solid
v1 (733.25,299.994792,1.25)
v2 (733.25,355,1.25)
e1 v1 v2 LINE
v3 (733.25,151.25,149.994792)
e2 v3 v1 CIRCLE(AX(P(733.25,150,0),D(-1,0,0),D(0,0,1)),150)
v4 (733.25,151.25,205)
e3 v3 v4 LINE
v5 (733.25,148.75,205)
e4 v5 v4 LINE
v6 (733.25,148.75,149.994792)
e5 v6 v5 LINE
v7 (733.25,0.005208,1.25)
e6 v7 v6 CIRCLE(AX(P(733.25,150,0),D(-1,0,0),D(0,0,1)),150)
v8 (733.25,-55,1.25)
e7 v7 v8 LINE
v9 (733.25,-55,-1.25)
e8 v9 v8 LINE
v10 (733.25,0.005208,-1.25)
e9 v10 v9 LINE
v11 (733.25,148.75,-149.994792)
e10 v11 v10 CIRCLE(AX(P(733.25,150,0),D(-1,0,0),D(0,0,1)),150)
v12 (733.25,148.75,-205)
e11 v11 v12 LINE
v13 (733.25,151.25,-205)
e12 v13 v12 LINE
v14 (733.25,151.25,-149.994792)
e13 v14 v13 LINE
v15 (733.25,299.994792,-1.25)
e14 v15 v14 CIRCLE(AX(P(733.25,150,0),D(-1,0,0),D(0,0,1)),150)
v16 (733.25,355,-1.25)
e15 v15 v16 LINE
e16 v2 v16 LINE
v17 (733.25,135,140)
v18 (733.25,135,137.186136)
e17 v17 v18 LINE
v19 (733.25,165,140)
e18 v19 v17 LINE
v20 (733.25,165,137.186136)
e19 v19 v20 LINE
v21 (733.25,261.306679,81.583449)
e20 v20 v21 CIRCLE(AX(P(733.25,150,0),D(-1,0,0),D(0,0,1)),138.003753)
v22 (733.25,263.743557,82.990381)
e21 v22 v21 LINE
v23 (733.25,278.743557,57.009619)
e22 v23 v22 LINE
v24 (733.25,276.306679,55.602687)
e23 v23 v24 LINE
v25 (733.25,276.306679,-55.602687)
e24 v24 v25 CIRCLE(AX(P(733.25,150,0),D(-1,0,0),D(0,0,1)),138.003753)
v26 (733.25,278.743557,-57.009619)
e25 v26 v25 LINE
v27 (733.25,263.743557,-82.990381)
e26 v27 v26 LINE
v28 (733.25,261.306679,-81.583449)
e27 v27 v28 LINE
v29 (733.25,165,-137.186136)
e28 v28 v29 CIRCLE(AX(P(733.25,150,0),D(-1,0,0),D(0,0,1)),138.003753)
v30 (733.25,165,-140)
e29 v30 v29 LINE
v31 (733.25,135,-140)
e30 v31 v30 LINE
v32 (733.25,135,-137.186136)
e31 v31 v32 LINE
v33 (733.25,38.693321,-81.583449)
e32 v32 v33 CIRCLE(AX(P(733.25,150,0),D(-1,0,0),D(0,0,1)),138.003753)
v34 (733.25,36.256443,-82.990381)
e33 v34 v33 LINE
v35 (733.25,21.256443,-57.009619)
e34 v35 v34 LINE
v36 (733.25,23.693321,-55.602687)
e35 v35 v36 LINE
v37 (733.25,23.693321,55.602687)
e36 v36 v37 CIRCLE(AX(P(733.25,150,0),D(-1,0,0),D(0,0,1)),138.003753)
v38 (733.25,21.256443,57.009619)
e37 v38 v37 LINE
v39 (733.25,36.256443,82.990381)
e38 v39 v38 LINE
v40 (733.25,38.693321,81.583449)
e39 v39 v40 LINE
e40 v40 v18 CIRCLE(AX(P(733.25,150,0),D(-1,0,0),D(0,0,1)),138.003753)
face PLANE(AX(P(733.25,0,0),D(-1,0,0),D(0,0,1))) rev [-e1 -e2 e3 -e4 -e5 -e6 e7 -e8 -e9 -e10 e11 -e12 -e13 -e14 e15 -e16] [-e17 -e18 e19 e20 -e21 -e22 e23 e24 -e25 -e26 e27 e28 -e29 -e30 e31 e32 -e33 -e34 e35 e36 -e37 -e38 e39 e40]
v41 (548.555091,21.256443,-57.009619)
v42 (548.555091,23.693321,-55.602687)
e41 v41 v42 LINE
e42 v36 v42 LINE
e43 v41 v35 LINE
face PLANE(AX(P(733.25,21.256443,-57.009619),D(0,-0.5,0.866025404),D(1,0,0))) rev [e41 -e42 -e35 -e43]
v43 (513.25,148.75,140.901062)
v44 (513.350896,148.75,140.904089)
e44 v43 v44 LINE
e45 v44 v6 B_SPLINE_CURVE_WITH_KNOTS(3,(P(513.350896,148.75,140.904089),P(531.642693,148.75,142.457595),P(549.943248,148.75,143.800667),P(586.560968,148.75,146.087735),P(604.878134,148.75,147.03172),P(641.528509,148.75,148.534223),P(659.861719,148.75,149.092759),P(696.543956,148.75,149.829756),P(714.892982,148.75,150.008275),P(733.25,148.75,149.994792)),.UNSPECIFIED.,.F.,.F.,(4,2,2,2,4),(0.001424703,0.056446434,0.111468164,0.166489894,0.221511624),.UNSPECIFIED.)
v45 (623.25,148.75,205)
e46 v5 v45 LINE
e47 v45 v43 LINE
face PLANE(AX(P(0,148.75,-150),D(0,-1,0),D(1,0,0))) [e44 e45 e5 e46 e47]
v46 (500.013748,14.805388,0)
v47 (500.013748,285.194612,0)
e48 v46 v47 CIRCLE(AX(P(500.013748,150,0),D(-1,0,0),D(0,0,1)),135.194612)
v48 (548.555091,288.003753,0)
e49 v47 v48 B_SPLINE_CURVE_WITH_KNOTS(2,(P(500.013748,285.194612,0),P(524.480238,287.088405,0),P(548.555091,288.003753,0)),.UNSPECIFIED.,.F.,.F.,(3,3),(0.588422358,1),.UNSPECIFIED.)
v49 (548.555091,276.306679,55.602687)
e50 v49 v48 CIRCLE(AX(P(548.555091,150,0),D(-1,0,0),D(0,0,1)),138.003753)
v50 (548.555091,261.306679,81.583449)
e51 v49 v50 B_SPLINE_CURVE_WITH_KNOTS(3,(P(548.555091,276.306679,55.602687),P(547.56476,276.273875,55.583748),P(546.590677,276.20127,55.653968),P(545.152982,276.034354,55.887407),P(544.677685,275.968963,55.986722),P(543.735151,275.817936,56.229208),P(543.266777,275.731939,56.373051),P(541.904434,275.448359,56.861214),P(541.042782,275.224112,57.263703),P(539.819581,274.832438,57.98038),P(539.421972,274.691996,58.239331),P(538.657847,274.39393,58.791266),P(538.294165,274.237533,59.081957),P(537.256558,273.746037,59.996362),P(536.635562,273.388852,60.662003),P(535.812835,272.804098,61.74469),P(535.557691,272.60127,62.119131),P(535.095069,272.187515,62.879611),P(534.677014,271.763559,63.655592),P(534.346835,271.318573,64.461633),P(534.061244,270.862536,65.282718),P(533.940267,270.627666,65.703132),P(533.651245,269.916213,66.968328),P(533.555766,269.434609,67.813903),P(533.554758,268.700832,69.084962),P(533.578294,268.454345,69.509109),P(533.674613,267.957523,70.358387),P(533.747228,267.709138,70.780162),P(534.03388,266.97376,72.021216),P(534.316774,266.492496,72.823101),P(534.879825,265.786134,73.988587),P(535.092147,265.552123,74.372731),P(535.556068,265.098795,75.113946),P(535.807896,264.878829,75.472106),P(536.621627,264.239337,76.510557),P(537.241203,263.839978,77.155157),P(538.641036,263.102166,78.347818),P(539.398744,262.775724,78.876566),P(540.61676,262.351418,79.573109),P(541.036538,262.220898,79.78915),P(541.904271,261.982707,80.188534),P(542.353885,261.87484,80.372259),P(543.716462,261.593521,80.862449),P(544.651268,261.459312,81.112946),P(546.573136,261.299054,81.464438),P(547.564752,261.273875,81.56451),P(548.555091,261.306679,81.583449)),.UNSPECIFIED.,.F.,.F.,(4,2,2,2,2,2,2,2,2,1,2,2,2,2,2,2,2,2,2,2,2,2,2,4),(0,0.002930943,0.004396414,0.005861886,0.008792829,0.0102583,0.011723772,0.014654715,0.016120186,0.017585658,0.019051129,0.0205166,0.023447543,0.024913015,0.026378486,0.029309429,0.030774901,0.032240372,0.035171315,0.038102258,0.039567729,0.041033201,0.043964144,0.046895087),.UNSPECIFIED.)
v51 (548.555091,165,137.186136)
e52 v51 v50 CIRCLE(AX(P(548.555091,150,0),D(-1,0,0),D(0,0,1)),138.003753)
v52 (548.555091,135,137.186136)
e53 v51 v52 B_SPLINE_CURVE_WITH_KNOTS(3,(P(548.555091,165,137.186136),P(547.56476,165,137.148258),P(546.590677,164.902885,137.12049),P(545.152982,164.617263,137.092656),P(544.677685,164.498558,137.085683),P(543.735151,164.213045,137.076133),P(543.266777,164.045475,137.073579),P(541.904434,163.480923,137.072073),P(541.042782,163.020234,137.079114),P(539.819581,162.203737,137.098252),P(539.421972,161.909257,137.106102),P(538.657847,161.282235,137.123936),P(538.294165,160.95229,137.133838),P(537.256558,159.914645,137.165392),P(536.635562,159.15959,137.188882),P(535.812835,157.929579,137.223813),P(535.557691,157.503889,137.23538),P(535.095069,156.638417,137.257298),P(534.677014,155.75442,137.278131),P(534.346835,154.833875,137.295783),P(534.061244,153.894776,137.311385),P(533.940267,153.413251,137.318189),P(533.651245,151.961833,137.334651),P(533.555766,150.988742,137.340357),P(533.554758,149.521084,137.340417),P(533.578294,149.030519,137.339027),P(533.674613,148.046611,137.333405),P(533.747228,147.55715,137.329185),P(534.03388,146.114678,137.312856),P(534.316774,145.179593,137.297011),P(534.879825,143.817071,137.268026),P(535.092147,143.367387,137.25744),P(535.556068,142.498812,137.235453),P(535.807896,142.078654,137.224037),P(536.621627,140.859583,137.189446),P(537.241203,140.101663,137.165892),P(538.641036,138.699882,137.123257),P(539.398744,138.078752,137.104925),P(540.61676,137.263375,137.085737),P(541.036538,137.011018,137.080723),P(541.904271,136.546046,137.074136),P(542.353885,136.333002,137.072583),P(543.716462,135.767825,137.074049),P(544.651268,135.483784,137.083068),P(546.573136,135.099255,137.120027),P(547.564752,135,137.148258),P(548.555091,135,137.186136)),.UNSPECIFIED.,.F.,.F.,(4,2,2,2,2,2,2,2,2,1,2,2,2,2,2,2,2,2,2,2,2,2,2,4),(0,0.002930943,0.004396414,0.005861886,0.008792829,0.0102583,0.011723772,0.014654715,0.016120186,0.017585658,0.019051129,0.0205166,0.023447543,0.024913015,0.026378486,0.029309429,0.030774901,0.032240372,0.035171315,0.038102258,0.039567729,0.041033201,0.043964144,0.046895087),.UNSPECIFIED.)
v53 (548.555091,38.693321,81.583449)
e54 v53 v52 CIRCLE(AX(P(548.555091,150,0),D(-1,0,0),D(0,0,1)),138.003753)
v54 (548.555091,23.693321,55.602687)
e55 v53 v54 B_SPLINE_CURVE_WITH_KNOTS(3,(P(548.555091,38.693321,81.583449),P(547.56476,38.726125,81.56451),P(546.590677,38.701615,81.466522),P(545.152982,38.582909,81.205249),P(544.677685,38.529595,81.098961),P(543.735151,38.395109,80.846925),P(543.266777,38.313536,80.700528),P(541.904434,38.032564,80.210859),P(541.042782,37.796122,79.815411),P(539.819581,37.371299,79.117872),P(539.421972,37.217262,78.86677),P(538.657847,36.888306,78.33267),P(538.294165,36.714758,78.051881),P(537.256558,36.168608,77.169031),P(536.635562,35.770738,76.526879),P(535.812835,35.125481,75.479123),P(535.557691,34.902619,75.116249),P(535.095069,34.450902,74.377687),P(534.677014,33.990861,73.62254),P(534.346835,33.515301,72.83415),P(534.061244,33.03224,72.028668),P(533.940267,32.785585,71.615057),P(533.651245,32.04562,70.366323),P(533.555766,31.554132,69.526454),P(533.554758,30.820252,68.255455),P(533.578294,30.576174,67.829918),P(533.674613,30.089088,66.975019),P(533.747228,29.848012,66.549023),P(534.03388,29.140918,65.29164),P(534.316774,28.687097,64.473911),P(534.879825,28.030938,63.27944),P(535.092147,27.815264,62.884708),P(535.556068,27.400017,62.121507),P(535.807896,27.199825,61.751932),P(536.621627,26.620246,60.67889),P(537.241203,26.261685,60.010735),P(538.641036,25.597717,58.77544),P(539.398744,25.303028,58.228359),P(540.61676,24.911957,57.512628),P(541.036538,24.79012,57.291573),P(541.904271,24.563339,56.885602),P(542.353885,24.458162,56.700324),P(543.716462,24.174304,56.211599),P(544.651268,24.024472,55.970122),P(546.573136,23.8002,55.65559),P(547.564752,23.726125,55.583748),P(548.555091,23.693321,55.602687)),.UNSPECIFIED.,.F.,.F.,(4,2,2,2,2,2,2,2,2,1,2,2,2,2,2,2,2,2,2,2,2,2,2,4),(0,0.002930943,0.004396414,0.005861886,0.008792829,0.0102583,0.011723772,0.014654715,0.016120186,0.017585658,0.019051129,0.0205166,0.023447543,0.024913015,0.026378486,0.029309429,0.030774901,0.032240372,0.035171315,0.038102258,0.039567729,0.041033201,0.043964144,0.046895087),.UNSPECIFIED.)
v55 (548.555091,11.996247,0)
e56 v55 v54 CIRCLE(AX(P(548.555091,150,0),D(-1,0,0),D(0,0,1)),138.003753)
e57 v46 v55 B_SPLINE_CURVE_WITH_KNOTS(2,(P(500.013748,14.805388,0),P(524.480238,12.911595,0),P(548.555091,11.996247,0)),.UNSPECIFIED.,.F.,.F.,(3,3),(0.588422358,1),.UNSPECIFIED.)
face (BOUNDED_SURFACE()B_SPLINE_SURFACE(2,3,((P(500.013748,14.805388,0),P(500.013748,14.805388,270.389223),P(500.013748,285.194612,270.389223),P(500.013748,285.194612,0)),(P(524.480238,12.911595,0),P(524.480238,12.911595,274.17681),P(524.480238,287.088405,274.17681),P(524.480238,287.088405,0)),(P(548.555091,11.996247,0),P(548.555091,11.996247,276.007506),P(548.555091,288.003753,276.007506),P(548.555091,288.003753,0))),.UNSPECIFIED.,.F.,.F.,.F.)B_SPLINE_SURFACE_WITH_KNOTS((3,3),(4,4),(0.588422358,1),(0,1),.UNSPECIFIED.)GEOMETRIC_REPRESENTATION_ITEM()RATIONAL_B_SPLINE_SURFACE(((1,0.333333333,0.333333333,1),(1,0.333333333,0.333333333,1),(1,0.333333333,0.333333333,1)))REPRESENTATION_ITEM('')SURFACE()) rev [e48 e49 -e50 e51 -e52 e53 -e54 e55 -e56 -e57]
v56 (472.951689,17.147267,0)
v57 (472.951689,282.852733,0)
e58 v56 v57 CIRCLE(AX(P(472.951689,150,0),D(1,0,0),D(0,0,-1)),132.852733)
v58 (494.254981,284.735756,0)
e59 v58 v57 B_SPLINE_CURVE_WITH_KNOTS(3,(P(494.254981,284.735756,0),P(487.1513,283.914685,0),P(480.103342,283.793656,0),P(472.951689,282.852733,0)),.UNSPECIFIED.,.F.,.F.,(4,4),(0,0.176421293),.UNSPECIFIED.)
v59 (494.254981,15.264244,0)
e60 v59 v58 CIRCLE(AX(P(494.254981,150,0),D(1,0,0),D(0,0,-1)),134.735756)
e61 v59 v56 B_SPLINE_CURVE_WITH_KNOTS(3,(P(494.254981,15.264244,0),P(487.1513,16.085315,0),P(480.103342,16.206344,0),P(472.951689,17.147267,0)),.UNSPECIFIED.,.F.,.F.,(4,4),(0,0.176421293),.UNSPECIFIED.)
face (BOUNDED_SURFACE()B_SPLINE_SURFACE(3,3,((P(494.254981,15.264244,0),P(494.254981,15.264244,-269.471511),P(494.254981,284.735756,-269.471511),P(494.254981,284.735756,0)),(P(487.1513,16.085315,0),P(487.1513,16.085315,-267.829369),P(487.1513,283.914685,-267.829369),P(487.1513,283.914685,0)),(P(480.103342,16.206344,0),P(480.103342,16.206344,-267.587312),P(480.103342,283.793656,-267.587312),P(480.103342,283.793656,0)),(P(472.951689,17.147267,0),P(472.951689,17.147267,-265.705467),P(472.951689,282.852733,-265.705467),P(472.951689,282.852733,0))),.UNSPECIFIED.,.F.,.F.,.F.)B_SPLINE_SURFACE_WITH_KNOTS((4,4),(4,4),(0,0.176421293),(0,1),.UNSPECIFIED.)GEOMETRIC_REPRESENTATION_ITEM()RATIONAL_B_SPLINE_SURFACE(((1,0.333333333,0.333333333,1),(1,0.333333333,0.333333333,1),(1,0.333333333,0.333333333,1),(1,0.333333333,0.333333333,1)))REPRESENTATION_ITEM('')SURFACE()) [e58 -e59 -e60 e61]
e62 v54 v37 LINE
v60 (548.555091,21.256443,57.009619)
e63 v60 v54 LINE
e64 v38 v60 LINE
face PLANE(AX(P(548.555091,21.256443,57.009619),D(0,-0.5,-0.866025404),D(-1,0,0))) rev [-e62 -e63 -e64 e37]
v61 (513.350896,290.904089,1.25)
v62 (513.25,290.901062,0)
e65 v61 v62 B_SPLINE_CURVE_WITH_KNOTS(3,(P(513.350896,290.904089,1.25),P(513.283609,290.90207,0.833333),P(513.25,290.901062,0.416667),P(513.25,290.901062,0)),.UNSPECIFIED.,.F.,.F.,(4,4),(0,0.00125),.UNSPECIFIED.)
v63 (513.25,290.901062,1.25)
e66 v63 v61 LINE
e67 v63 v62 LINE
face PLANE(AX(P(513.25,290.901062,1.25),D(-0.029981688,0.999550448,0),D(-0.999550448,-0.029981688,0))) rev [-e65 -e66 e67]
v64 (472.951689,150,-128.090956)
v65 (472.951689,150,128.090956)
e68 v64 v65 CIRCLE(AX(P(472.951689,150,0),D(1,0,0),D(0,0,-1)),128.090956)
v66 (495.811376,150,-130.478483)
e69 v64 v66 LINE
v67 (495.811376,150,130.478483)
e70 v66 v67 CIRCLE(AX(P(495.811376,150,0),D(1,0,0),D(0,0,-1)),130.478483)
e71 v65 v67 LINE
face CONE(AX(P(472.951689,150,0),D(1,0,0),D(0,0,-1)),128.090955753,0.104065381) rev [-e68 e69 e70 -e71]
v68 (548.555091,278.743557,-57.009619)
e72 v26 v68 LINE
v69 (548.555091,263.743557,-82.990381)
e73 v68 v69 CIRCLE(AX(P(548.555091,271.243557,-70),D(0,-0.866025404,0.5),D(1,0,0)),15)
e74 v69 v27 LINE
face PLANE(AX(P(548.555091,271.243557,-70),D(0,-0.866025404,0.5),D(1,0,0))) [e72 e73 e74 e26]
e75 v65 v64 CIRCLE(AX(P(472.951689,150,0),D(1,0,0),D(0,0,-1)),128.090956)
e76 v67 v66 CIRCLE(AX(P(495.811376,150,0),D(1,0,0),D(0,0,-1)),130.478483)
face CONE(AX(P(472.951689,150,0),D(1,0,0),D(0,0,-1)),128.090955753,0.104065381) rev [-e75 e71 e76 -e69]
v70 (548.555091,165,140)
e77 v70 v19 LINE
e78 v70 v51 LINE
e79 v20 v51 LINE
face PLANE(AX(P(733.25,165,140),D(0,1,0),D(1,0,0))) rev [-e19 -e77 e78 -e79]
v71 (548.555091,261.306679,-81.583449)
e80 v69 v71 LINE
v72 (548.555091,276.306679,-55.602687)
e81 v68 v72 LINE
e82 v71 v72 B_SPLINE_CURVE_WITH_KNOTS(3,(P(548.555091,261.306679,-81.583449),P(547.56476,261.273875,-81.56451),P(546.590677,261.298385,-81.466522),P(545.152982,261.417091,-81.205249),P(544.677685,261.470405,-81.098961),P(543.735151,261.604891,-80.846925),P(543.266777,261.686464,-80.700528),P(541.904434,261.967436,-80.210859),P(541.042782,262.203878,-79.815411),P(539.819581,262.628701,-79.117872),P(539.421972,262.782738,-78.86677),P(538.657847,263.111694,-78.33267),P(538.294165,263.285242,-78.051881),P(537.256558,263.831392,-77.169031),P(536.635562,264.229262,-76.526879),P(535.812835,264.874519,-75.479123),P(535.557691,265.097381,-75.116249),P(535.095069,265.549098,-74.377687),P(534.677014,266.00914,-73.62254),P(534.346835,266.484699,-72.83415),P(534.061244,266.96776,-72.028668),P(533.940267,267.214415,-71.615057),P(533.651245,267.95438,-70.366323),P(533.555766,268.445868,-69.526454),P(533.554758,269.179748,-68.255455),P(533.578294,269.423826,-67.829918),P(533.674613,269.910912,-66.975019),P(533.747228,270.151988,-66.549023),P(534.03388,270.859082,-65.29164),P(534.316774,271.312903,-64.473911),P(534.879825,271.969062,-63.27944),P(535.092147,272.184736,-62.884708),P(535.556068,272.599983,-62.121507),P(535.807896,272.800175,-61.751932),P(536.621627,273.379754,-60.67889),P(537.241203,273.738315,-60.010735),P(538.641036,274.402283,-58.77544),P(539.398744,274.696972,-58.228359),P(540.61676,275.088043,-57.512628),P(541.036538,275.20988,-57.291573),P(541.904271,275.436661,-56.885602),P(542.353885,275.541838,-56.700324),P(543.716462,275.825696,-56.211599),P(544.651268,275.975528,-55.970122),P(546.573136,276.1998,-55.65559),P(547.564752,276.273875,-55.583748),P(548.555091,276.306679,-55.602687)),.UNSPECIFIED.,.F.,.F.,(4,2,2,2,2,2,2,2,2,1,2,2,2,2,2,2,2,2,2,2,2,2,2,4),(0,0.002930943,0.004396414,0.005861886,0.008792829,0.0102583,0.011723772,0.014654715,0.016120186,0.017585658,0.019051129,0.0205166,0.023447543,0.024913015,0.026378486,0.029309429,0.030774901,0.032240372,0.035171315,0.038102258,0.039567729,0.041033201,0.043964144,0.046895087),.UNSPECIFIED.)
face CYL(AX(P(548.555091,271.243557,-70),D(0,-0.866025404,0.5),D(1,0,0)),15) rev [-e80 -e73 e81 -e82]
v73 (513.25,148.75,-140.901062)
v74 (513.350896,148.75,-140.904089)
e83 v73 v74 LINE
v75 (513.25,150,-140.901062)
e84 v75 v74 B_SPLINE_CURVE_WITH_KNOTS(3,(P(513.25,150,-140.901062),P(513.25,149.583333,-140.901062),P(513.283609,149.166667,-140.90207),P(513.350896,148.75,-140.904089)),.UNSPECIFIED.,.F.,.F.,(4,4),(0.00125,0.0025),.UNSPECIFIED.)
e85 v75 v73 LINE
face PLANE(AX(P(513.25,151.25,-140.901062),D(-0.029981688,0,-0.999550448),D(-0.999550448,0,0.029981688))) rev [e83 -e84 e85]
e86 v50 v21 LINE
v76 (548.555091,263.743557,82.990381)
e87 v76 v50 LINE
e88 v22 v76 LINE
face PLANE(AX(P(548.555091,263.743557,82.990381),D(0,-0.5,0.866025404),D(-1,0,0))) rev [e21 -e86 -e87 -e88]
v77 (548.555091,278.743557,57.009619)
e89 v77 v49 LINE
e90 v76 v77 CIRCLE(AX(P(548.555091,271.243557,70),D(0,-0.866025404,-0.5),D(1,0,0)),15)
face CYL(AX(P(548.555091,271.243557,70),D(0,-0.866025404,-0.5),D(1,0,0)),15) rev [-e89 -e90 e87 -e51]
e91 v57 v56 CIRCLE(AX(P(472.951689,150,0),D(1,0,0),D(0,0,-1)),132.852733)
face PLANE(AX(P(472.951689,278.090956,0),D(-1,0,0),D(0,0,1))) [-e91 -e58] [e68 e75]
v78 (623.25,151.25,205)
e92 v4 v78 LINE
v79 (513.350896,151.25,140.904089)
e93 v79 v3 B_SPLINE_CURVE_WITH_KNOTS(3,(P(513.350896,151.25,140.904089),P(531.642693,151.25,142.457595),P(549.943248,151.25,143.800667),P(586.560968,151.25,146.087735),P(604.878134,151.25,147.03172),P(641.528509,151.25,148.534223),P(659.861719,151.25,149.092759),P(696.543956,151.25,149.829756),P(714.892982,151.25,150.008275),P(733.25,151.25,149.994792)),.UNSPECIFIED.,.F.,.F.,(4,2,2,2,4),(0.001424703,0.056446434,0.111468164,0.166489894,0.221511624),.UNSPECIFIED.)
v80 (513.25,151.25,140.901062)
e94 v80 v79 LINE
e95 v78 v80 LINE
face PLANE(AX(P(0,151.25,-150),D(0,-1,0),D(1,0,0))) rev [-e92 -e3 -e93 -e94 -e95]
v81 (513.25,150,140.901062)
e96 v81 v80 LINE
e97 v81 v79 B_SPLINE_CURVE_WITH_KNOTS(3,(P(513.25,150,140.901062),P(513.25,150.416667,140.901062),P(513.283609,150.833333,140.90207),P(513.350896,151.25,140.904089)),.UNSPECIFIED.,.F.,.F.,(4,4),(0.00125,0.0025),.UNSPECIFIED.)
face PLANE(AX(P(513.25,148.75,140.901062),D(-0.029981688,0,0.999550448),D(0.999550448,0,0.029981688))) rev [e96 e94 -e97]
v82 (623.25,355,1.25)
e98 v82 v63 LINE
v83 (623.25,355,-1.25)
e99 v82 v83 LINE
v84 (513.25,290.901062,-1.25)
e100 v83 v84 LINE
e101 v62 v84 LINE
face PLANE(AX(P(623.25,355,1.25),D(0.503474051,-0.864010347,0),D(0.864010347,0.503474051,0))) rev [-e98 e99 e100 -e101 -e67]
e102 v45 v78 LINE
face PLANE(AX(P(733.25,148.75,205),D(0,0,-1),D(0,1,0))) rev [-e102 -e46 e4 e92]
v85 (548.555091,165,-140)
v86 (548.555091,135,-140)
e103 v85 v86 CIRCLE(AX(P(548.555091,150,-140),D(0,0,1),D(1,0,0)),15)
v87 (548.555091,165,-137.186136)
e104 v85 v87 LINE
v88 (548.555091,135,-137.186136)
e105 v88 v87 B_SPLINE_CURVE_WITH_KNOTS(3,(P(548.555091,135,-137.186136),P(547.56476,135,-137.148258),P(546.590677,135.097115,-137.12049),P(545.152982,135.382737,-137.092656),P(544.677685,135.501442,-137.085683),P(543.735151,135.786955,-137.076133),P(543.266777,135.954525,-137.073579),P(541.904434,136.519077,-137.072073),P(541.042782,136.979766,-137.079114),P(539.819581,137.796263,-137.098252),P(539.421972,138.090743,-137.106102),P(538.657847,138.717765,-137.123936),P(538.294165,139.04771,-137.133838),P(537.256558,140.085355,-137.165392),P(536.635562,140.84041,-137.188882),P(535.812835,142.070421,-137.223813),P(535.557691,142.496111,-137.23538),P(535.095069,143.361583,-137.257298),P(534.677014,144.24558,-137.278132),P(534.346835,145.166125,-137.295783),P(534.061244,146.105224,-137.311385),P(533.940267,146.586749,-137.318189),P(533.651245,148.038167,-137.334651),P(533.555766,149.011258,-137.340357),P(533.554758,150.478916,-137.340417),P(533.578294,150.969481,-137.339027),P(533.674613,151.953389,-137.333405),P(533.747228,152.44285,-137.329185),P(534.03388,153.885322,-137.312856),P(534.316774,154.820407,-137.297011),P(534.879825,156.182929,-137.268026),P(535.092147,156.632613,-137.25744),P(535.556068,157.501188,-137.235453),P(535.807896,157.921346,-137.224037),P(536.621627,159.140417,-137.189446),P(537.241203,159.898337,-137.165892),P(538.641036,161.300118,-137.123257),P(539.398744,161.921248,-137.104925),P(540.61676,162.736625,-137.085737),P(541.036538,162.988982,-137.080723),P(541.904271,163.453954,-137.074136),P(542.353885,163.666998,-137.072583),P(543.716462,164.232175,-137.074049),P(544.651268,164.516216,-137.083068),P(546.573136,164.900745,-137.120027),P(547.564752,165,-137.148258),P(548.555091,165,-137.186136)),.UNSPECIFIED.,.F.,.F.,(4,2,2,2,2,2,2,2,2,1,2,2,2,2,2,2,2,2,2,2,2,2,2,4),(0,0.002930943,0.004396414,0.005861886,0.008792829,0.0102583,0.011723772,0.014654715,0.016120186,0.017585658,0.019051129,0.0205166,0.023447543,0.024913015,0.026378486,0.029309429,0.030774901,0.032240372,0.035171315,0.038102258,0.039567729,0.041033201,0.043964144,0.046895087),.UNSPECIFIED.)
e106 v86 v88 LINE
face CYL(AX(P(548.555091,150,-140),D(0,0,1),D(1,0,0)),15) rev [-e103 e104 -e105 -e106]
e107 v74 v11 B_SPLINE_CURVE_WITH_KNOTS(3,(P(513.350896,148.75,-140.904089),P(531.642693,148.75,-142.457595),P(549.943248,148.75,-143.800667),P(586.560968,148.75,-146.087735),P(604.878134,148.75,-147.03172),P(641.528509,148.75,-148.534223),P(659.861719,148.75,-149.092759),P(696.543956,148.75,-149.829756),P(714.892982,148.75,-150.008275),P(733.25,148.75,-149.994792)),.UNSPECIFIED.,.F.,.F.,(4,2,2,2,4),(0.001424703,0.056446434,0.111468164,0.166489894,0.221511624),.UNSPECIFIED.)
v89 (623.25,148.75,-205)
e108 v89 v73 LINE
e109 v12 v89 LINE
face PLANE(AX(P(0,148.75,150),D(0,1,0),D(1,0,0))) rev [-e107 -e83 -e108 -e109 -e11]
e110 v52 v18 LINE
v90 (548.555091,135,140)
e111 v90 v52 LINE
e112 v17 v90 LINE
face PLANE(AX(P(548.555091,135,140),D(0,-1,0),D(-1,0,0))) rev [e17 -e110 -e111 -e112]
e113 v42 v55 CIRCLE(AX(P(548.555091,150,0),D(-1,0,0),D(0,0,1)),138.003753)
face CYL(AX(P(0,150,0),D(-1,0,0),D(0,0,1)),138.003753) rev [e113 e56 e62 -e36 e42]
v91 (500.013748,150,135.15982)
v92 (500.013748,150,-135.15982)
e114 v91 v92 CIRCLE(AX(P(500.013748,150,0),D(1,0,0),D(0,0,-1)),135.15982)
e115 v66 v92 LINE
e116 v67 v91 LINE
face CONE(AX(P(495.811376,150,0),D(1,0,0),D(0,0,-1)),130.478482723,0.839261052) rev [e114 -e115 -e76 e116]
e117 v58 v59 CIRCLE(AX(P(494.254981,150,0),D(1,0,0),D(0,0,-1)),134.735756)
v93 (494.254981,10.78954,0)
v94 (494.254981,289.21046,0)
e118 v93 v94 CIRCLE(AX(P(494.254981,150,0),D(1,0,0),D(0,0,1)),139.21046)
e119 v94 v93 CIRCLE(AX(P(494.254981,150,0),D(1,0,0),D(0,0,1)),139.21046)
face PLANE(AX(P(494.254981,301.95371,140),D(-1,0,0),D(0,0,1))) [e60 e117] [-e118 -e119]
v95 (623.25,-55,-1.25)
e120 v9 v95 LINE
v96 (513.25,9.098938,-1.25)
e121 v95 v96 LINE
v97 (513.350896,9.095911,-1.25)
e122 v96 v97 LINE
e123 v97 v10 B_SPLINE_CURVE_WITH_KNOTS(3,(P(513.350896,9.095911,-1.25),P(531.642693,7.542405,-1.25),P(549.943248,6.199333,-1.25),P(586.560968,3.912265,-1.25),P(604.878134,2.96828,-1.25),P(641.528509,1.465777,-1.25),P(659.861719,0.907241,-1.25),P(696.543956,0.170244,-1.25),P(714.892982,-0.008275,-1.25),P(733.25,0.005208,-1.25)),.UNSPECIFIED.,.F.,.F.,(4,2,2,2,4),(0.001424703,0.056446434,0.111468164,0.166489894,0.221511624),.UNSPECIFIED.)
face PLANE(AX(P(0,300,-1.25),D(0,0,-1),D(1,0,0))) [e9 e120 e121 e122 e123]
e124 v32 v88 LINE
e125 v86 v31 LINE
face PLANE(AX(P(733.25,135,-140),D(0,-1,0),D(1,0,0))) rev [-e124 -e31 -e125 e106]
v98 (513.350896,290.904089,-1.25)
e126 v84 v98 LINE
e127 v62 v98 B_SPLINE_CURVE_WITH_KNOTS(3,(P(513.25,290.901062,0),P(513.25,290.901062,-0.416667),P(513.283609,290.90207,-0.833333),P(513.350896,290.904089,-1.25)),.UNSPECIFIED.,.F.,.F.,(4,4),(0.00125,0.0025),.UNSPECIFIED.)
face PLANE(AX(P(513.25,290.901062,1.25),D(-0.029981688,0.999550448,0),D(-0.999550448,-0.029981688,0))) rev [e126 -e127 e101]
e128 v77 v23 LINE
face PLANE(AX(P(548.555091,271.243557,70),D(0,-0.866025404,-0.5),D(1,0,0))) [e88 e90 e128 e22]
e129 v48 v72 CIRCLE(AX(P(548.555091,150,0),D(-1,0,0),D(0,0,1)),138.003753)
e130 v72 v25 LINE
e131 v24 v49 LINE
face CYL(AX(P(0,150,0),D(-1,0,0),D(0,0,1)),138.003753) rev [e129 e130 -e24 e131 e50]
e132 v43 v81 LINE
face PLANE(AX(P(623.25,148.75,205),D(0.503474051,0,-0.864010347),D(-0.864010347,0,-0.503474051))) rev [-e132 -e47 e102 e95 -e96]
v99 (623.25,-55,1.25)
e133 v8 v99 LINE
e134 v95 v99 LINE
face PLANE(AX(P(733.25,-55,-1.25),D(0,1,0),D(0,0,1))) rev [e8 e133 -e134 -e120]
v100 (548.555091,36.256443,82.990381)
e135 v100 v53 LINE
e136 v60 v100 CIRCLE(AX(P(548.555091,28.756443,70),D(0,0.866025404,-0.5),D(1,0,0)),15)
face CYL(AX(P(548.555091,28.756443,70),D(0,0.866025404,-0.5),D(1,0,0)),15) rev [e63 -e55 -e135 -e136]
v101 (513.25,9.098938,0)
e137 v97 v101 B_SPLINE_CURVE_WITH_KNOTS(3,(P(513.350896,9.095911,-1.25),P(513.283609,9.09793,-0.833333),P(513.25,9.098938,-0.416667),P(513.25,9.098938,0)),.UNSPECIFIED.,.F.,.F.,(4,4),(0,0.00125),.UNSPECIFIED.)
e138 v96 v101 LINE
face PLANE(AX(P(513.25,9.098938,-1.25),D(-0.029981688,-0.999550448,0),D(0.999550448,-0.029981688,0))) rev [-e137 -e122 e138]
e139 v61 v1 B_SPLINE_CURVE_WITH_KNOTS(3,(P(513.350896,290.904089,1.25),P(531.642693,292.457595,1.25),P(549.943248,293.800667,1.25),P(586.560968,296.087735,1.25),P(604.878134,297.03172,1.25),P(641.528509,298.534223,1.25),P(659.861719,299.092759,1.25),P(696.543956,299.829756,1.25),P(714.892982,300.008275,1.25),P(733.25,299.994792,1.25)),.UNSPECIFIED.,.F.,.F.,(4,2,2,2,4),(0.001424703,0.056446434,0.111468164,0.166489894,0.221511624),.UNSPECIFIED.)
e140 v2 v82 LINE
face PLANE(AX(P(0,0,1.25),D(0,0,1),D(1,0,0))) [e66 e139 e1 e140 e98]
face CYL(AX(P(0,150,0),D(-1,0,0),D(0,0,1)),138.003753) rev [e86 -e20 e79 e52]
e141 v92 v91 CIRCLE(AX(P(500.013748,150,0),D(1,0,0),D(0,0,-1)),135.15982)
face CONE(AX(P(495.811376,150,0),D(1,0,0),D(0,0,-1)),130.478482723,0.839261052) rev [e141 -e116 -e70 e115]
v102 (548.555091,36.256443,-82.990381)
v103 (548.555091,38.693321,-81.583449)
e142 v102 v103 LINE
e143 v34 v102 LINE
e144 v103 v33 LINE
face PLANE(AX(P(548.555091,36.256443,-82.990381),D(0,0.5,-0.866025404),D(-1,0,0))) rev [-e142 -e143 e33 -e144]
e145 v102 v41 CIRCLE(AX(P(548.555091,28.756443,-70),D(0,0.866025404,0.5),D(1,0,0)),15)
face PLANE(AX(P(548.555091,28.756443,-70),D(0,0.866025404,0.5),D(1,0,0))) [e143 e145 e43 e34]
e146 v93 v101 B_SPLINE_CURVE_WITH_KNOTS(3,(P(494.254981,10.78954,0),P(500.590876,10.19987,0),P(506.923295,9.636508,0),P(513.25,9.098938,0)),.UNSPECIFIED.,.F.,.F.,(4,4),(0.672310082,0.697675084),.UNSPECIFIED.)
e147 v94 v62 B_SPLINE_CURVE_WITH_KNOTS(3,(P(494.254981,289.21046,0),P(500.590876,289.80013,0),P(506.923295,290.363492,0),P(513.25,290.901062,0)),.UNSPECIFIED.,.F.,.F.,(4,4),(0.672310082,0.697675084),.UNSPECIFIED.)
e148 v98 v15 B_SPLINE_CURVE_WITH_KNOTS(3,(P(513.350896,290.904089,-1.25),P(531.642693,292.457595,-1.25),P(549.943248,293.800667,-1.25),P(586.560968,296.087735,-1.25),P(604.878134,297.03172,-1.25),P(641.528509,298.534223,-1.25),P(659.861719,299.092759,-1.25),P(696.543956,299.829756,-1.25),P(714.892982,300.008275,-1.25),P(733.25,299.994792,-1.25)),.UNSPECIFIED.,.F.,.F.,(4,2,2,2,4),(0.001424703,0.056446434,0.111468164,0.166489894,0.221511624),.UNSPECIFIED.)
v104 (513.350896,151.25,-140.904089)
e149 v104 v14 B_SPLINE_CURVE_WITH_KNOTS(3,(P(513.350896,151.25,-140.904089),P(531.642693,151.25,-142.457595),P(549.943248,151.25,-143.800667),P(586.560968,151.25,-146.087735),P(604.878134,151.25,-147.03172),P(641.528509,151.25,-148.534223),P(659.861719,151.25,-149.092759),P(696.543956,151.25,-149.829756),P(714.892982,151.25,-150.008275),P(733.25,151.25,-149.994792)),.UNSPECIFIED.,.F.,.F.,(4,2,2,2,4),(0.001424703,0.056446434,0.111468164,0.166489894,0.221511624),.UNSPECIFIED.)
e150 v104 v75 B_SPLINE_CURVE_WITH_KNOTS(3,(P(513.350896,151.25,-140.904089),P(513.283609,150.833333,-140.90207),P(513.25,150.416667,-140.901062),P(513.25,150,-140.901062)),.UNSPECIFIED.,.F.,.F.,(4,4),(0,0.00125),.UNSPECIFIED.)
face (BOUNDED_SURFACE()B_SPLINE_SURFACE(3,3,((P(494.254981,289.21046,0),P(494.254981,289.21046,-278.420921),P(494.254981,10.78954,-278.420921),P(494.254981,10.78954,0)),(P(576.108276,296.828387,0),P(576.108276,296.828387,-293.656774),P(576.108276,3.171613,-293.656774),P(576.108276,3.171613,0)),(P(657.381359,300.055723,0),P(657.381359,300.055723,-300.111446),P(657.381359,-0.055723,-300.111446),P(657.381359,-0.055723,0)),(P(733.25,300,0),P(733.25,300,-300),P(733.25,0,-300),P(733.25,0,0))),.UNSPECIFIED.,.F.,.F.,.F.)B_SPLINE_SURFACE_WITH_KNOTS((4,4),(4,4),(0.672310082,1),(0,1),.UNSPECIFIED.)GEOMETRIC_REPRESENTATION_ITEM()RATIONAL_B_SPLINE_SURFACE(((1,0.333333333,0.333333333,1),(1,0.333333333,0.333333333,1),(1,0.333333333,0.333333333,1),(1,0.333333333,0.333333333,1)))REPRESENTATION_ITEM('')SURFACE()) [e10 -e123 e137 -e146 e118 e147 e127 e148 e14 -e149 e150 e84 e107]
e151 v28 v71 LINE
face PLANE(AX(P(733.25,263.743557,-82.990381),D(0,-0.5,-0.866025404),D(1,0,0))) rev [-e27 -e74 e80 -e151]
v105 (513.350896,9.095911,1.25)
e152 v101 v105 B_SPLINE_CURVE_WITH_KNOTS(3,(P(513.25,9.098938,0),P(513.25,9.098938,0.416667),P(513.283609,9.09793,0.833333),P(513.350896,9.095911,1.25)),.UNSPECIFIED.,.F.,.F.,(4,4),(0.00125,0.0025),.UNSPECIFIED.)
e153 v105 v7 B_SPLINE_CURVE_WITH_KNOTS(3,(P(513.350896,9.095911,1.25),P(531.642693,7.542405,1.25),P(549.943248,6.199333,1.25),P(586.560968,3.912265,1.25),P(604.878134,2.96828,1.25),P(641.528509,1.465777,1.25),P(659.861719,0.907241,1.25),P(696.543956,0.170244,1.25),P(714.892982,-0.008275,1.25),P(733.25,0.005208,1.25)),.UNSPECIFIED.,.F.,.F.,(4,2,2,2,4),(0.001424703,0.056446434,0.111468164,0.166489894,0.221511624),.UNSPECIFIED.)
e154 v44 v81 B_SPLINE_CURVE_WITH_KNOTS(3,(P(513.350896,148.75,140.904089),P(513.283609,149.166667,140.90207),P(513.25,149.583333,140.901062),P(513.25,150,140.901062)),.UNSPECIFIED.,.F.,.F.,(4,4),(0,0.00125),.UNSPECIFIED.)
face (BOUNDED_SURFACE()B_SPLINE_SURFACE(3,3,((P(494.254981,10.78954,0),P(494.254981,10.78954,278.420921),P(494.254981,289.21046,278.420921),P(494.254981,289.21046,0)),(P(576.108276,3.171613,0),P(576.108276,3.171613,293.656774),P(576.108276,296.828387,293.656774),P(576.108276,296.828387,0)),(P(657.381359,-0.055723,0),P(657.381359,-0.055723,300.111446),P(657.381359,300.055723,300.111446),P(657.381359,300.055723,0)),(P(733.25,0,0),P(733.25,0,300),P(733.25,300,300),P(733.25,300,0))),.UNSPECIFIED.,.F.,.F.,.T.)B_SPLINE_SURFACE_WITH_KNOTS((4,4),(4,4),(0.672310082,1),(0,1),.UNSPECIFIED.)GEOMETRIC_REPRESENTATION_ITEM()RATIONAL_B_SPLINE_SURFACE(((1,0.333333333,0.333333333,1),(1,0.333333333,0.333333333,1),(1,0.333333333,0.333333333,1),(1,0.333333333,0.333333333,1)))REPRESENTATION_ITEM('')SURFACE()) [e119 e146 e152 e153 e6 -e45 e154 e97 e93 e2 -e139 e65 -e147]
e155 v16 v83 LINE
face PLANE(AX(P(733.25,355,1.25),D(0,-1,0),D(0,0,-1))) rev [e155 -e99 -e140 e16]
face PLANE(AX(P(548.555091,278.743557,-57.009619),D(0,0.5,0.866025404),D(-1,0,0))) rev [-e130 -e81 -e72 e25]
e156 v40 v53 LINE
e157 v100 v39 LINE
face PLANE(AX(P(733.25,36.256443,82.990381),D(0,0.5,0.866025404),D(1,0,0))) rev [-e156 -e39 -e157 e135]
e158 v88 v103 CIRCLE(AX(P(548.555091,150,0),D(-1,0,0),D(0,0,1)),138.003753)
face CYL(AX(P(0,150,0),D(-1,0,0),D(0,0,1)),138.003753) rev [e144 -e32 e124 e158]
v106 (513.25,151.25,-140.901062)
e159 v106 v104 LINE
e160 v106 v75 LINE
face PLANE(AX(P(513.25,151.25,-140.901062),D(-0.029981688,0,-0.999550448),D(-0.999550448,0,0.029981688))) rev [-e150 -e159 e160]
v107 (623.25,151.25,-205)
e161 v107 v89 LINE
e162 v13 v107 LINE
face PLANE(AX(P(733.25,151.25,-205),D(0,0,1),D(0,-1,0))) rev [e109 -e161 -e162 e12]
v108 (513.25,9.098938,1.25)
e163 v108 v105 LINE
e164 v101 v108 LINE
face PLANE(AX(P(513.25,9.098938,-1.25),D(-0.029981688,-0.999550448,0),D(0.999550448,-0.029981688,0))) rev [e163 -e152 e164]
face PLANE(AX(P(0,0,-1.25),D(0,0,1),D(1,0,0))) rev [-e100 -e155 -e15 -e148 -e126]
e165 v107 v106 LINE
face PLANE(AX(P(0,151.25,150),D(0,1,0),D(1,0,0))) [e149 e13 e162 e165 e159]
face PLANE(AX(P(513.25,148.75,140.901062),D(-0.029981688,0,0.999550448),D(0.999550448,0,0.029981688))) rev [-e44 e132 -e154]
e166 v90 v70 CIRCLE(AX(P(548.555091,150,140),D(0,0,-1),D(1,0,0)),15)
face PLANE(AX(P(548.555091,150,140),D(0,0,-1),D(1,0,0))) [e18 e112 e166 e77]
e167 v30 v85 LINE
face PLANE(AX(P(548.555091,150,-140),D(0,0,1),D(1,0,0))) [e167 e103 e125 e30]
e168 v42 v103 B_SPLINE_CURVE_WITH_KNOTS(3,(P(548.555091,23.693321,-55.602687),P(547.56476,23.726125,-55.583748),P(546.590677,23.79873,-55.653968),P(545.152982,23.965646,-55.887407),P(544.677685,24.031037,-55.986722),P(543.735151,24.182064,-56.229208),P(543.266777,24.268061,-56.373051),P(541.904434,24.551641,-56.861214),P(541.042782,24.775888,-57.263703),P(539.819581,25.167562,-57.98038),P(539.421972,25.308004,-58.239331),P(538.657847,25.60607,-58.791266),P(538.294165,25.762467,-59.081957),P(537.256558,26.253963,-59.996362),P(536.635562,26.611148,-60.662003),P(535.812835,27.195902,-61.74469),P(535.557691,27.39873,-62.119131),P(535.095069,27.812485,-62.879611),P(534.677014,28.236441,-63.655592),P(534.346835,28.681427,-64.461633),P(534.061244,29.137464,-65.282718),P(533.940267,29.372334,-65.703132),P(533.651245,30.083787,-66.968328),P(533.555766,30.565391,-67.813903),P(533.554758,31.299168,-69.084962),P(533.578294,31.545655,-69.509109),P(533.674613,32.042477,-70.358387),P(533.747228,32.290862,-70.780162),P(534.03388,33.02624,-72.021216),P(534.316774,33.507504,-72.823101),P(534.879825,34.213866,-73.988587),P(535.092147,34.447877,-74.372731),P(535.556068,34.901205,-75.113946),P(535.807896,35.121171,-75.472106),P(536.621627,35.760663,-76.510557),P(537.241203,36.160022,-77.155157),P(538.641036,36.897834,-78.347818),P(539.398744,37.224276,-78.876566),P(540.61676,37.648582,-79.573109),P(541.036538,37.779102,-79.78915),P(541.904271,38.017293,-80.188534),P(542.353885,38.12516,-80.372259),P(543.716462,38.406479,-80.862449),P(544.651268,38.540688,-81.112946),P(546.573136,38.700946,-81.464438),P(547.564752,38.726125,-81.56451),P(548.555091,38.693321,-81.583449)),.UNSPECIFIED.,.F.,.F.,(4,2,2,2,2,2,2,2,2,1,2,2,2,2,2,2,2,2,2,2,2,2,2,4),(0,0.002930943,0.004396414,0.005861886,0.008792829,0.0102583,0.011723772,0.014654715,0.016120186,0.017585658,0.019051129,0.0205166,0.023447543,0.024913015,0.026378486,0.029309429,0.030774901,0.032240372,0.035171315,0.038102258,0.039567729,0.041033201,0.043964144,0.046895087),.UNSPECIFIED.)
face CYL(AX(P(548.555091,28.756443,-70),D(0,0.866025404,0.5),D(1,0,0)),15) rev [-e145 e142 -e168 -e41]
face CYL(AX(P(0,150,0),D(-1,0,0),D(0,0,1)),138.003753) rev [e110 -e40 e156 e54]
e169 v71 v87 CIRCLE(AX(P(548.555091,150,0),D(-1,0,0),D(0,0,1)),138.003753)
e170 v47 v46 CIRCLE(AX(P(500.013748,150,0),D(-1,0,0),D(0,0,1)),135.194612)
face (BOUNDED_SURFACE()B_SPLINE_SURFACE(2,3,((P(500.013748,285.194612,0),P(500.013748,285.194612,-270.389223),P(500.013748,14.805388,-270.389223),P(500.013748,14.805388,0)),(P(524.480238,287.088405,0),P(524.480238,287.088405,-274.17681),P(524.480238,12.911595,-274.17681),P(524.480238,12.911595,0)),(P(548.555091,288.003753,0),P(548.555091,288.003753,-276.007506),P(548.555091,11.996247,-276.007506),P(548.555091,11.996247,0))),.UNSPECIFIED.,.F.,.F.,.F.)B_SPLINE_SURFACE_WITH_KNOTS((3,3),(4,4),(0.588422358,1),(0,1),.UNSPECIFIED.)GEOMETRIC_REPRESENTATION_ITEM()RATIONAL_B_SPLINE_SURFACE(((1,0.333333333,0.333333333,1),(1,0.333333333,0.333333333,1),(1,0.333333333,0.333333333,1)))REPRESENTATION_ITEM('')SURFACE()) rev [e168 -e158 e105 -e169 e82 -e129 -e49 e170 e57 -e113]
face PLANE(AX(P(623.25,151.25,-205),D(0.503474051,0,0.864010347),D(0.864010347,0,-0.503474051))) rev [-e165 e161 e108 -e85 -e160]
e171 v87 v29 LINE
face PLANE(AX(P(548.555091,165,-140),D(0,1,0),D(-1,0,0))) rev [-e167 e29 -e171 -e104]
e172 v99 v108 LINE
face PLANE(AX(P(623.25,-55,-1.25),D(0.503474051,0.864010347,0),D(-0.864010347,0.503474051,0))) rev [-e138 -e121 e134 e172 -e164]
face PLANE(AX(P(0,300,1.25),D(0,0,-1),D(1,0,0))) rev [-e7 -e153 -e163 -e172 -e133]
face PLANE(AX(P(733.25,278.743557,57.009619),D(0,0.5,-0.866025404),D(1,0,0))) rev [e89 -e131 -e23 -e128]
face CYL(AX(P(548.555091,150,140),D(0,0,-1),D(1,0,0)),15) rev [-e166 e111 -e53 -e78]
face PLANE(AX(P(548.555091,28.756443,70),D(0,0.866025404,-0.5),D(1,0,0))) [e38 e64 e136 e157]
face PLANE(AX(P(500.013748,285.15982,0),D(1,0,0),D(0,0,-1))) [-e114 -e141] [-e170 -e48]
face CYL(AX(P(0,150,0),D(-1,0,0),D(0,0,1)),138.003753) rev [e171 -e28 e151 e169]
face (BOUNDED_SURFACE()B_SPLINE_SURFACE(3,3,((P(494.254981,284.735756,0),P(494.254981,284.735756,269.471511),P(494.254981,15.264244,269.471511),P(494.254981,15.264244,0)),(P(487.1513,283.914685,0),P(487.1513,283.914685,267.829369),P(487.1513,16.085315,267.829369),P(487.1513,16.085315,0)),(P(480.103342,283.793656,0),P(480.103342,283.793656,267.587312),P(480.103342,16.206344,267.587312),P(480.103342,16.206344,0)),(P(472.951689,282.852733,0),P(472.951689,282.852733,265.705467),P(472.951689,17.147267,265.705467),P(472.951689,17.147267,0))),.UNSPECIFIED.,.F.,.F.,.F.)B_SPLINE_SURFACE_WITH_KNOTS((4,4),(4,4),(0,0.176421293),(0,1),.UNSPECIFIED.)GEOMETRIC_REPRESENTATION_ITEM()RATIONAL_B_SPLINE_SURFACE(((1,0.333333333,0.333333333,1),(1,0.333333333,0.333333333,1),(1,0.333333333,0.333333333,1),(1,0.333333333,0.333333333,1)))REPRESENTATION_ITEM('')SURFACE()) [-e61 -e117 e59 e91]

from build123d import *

# Parameters (mm, degrees)
CUT_EXTRUDE1_DEPTH      = 140
CIRPATTERN3_COUNT       = 6
BOSS_EXTRUDE2_DEPTH     = 1.25
CIRPATTERN5_COUNT       = 4
CUT_EXTRUDE2_DEPTH      = 140
CUT_EXTRUDE2_DEPTH_BACK = 160
SKETCH7_W               = 64.782558885
SKETCH7_H               = 314.406040355


with BuildPart() as part:
    # Sketch2 → Revolve3 (revolve)
    with BuildSketch(Plane.XY, mode=Mode.PRIVATE) as revolve3_sk:
        with BuildLine():
            add(Edge.make_bspline(
                [(450.637981389, 284.73247383), (547.084546243, 295.579175512), (643.913977944, 300.065614523), (733.25, 300)],
                knots=[0.61414211, 0.61414211, 0.61414211, 0.61414211, 1, 1, 1, 1], degree=3))
            Line((450.637981389, 284.73247383), (450.637981389, 280.422668446))
            add(Edge.make_bspline(
                [(429.254980688, 277.779677975), (436.406633809, 278.720600606), (443.534300709, 279.601597429), (450.637981389, 280.422668446)],
                knots=[0, 0, 0, 0, 0.176421293, 0.176421293, 0.176421293, 0.176421293], degree=3))
            Line((429.254980688, 277.779677975), (429.254980688, 273.462123081))
            Line((429.254980688, 273.462123081), (452.579811784, 276.562541937))
            Line((452.579811784, 276.562541937), (456.493793174, 281.086536072))
            add(Edge.make_bspline(
                [(456.493793174, 281.086536072), (503.218855637, 286.280028028), (548.555090765, 288.003752879)],
                knots=[0.224943096, 0.224943096, 0.224943096, 1, 1, 1], degree=2))
            Line((548.555090765, 288.003752879), (733.25, 288.003752879))
            Line((733.25, 288.003752879), (733.25, 300))
        make_face()
    revolve(revolve3_sk.sketch.rotate(Axis((0, 150, 0), (1, 0, 0)), 90), axis=Axis((0, 150, 0), (1, 0, 0)))

    # Sketch5 → Cut-Extrude1 (cut)
    with BuildSketch(Plane.XY):
        with BuildLine():
            Line((548.555090765, 165), (733.25, 165))
            Line((733.25, 165), (733.25, 135))
            Line((733.25, 135), (548.555090765, 135))
            ThreePointArc((548.555090765, 135), (533.555090765, 150), (548.555090765, 165))
        make_face()
    cut_extrude1 = extrude(amount=-CUT_EXTRUDE1_DEPTH, mode=Mode.SUBTRACT)

    # CirPattern3: Cut-Extrude1 ×6 about axis
    cirpattern3_axis = Axis((0, 150, 0), (1, 0, 0))
    for i in range(1, CIRPATTERN3_COUNT):
        add(cut_extrude1.rotate(cirpattern3_axis, i * 360 / CIRPATTERN3_COUNT), mode=Mode.SUBTRACT)

    # Sketch6 → Boss-Extrude2 (add, symmetric)
    with BuildSketch(Plane.XY):
        Polygon((733.25, 297.5), (733.25, 355), (623.25, 355), (513.25, 290.901062134), align=None)
    boss_extrude2 = extrude(amount=BOSS_EXTRUDE2_DEPTH, both=True)

    # CirPattern5: Boss-Extrude2 ×4 about axis
    cirpattern5_axis = Axis((0, 150, 0), (1, 0, 0))
    for i in range(1, CIRPATTERN5_COUNT):
        add(boss_extrude2.rotate(cirpattern5_axis, i * 360 / CIRPATTERN5_COUNT))

    # Sketch7 → Cut-Extrude2 (cut, two sides: drawn at the far end of the back side and taken through both)
    with BuildSketch(Plane.XY.offset(-CUT_EXTRUDE2_DEPTH_BACK)):
        with Locations((461.863701246, 144.750690011)):
            Rectangle(SKETCH7_W, SKETCH7_H)
    extrude(amount=CUT_EXTRUDE2_DEPTH + CUT_EXTRUDE2_DEPTH_BACK, mode=Mode.SUBTRACT)


with BuildPart() as body_2:
    # of the pieces the cut leaves, the one that is kept (cut_extrude2_keep)
    add(part.part.solids().sort_by_distance((494.254980688, 150, 139.21046037))[0])

    # Sketch8 → Revolve4 (revolve)
    with BuildSketch(Plane.XY, mode=Mode.PRIVATE) as revolve4_sk:
        with BuildLine():
            Line((500.01374771, 285.159819571), (500.01374771, 287.937524413))
            Line((500.01374771, 287.937524413), (494.254980688, 287.492248924))
            Line((494.254980688, 287.492248924), (494.254980688, 284.735755541))
            add(Edge.make_bspline(
                [(472.951688948, 282.852733411), (480.103342069, 283.793656042), (487.151300008, 283.914684525), (494.254980688, 284.735755541)],
                knots=[0, 0, 0, 0, 0.176421293, 0.176421293, 0.176421293, 0.176421293], degree=3))
            Line((472.951688948, 282.852733411), (472.951688948, 278.090955753))
            Line((472.951688948, 278.090955753), (495.811376327, 280.478482723))
            Line((495.811376327, 280.478482723), (500.01374771, 285.159819571))
        make_face()
    revolve(revolve4_sk.sketch.rotate(Axis((733.25, 150, 0), (-1, 0, 0)), 90), axis=Axis((733.25, 150, 0), (-1, 0, 0)))


solid = body_2.part
